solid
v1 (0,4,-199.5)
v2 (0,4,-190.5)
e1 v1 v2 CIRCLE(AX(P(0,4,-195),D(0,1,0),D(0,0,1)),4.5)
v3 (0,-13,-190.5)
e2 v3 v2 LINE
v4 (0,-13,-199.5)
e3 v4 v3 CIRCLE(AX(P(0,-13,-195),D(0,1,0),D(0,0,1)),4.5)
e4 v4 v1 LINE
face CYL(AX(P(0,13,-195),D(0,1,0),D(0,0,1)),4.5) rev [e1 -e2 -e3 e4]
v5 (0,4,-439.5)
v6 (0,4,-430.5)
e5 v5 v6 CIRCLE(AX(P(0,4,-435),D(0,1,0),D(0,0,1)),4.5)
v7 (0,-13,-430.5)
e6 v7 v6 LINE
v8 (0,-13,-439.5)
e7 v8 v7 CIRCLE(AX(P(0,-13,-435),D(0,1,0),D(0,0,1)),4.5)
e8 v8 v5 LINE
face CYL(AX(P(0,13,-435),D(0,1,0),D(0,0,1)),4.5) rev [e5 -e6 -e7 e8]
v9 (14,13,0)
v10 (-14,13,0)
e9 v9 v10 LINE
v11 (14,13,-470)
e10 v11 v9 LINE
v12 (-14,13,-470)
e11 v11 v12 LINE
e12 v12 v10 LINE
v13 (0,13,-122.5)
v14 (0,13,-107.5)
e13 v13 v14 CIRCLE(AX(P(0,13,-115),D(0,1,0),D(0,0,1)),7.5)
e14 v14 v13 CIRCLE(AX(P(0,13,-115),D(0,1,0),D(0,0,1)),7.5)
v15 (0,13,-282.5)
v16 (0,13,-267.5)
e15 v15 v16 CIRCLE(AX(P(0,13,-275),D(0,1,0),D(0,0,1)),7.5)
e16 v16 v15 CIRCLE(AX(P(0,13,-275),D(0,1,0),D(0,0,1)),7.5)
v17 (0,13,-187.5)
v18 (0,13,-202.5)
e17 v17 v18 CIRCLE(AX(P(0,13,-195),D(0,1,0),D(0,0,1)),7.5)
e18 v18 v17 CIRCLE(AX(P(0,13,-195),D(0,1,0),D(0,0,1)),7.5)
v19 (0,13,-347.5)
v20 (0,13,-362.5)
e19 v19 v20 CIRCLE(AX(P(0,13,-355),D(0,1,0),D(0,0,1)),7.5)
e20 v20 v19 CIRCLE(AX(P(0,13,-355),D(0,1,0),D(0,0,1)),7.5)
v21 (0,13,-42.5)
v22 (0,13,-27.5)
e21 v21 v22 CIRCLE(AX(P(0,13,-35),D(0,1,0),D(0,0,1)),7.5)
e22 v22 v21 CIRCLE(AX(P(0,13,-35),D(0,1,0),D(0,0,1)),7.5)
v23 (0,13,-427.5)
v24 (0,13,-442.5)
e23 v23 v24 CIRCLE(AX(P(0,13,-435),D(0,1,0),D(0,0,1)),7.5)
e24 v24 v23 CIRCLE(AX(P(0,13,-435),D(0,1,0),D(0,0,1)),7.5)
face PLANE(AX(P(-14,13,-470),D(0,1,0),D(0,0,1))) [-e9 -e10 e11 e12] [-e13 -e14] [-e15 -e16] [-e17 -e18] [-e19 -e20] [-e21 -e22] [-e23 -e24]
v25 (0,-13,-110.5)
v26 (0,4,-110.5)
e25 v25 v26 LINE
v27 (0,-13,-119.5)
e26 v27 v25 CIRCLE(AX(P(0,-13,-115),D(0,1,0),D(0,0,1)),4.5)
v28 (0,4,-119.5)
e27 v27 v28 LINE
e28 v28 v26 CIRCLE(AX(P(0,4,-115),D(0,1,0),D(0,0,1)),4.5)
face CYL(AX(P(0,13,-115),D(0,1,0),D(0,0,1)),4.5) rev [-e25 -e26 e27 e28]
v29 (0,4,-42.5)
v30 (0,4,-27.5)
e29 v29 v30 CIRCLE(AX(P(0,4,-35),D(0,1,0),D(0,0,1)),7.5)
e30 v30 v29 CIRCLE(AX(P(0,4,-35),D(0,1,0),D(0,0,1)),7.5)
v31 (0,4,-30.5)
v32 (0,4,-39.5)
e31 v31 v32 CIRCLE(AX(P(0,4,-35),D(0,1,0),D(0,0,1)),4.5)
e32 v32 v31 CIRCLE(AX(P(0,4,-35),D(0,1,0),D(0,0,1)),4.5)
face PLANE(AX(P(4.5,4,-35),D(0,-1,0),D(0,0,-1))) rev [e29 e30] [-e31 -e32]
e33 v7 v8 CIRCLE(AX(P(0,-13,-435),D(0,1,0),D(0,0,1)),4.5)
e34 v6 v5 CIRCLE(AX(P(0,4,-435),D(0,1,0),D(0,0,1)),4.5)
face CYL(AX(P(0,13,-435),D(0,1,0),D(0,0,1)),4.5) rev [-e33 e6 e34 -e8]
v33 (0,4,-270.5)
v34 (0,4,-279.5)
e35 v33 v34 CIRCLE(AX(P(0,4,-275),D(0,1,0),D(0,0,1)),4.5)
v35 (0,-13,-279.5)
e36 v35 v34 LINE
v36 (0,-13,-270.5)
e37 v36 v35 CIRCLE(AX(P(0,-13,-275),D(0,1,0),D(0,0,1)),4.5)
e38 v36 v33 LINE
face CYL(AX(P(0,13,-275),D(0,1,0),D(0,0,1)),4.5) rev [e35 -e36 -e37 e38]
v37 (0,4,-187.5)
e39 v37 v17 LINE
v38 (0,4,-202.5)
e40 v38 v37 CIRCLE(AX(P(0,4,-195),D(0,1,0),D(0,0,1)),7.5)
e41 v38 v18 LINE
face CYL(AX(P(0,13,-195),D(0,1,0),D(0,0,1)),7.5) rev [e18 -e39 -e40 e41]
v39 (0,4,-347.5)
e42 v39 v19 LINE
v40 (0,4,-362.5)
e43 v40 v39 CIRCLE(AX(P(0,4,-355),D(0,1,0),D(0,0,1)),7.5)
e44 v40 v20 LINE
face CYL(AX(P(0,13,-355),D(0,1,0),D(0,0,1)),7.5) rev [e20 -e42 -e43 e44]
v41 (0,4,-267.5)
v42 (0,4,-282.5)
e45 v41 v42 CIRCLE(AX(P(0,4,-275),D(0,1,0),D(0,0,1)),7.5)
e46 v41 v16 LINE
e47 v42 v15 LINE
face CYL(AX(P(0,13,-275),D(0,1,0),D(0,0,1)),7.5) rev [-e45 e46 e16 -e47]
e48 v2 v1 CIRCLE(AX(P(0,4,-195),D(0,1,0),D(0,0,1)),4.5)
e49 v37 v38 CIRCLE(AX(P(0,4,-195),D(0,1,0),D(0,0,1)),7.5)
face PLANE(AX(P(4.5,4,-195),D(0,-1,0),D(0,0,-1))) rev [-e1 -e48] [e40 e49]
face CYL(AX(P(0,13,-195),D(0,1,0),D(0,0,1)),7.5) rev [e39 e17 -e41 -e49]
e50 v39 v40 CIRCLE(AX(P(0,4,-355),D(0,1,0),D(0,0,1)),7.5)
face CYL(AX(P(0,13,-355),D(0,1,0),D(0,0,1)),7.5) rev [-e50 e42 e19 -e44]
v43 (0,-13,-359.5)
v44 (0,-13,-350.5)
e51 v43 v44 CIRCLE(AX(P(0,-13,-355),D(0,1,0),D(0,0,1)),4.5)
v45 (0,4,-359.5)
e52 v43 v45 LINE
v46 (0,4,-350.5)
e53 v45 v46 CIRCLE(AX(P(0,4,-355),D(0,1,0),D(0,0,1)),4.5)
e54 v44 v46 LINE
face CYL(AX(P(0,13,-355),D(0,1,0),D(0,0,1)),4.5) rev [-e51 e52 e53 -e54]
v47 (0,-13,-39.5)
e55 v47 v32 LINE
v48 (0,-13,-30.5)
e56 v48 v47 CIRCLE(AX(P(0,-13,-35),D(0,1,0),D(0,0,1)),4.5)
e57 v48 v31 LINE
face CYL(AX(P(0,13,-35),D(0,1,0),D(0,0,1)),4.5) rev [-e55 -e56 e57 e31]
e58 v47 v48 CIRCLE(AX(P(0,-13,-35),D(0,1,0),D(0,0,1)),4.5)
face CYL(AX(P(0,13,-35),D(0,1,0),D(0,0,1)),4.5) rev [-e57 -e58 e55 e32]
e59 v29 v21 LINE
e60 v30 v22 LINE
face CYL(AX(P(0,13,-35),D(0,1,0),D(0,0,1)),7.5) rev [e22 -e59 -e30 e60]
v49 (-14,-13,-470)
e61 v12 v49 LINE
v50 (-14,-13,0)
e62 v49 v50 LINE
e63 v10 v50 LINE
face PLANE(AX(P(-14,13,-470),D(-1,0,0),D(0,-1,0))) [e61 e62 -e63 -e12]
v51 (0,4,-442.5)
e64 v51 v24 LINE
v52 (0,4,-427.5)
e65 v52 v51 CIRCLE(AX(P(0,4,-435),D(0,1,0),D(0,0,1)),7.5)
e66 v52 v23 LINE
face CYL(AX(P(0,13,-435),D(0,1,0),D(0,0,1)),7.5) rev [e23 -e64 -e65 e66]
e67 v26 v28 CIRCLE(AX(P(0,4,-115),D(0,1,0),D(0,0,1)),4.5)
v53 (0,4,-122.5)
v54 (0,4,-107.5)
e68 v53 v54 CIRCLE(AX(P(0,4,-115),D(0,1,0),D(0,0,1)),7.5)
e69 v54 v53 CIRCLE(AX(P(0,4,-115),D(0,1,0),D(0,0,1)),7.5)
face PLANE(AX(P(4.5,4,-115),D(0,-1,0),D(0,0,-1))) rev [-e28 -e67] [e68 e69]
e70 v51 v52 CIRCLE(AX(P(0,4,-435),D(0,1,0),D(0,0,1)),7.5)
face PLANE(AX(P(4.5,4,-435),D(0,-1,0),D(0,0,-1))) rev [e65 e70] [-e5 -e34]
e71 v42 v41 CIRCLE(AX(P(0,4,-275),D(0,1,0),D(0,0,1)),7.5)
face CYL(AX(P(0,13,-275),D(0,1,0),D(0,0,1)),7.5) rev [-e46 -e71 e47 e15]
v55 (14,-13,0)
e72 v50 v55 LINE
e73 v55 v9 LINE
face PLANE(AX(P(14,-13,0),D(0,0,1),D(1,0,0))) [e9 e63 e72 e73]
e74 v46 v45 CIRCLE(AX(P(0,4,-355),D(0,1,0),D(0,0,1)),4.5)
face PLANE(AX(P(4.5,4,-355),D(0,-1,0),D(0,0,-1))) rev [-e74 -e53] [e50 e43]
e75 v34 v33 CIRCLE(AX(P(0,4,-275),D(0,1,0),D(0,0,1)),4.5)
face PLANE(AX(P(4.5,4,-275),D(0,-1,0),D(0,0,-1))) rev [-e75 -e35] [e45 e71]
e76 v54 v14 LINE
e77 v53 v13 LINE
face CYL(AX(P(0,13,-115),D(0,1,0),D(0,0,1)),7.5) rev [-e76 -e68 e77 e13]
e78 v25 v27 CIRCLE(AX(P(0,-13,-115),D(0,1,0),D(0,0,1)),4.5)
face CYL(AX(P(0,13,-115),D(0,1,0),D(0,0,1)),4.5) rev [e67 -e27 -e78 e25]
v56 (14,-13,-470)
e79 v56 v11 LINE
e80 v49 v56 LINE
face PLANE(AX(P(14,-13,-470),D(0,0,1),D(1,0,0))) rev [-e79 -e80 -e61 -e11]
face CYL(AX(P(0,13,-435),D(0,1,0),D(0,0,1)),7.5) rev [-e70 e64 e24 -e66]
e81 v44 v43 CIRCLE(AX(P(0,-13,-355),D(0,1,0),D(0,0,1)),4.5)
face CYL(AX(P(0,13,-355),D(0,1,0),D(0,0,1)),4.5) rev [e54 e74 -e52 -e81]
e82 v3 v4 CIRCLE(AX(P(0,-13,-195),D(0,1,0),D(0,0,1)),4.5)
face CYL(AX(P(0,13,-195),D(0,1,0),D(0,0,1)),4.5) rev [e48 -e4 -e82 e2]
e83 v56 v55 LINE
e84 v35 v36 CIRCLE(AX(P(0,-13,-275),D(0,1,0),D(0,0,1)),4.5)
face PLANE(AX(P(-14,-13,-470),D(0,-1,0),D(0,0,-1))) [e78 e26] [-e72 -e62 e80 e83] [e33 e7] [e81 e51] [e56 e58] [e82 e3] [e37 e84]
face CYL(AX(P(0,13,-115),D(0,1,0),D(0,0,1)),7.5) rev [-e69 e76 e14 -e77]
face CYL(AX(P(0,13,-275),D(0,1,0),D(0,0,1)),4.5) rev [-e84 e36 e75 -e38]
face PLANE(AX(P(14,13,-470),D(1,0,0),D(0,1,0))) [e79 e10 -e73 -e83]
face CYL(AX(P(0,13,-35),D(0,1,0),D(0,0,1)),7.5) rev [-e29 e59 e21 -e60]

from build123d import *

# Parameters (mm, degrees)
SKETCH1_W                                            = 28
SKETCH1_H                                            = 26
BOSS_EXTRUDE1_DEPTH                                  = 470
HOLE_SIZE_PER_SOCKET_HEAD_CAP_SCREW_TYPE_D           = 9
HOLE_SIZE_PER_SOCKET_HEAD_CAP_SCREW_TYPE_CBORE_D     = 15
HOLE_SIZE_PER_SOCKET_HEAD_CAP_SCREW_TYPE_CBORE_DEPTH = 9
LPATTERN1_COUNT                                      = 6
LPATTERN1_PITCH                                      = 80


with BuildPart() as part:
    # Sketch1 → Boss-Extrude1 (new body)
    with BuildSketch(Plane.XY):
        Rectangle(SKETCH1_W, SKETCH1_H)
    extrude(amount=-BOSS_EXTRUDE1_DEPTH)

    # Hole size per socket head cap screw type1 (through all)
    with Locations(Plane(origin=(0, 13, 0), x_dir=(-1, 0, 0), z_dir=(0, 1, 0))):
        with Locations((0, -35)):
            hole_size_per_socket_head_cap_screw_type = CounterBoreHole(HOLE_SIZE_PER_SOCKET_HEAD_CAP_SCREW_TYPE_D / 2, HOLE_SIZE_PER_SOCKET_HEAD_CAP_SCREW_TYPE_CBORE_D / 2, HOLE_SIZE_PER_SOCKET_HEAD_CAP_SCREW_TYPE_CBORE_DEPTH)

    # LPattern1: Hole size per socket head cap screw type1 ×6
    with Locations(*[(0, 0, -i * LPATTERN1_PITCH) for i in range(1, LPATTERN1_COUNT)]):
        add(hole_size_per_socket_head_cap_screw_type, mode=Mode.SUBTRACT)


solid = part.part
